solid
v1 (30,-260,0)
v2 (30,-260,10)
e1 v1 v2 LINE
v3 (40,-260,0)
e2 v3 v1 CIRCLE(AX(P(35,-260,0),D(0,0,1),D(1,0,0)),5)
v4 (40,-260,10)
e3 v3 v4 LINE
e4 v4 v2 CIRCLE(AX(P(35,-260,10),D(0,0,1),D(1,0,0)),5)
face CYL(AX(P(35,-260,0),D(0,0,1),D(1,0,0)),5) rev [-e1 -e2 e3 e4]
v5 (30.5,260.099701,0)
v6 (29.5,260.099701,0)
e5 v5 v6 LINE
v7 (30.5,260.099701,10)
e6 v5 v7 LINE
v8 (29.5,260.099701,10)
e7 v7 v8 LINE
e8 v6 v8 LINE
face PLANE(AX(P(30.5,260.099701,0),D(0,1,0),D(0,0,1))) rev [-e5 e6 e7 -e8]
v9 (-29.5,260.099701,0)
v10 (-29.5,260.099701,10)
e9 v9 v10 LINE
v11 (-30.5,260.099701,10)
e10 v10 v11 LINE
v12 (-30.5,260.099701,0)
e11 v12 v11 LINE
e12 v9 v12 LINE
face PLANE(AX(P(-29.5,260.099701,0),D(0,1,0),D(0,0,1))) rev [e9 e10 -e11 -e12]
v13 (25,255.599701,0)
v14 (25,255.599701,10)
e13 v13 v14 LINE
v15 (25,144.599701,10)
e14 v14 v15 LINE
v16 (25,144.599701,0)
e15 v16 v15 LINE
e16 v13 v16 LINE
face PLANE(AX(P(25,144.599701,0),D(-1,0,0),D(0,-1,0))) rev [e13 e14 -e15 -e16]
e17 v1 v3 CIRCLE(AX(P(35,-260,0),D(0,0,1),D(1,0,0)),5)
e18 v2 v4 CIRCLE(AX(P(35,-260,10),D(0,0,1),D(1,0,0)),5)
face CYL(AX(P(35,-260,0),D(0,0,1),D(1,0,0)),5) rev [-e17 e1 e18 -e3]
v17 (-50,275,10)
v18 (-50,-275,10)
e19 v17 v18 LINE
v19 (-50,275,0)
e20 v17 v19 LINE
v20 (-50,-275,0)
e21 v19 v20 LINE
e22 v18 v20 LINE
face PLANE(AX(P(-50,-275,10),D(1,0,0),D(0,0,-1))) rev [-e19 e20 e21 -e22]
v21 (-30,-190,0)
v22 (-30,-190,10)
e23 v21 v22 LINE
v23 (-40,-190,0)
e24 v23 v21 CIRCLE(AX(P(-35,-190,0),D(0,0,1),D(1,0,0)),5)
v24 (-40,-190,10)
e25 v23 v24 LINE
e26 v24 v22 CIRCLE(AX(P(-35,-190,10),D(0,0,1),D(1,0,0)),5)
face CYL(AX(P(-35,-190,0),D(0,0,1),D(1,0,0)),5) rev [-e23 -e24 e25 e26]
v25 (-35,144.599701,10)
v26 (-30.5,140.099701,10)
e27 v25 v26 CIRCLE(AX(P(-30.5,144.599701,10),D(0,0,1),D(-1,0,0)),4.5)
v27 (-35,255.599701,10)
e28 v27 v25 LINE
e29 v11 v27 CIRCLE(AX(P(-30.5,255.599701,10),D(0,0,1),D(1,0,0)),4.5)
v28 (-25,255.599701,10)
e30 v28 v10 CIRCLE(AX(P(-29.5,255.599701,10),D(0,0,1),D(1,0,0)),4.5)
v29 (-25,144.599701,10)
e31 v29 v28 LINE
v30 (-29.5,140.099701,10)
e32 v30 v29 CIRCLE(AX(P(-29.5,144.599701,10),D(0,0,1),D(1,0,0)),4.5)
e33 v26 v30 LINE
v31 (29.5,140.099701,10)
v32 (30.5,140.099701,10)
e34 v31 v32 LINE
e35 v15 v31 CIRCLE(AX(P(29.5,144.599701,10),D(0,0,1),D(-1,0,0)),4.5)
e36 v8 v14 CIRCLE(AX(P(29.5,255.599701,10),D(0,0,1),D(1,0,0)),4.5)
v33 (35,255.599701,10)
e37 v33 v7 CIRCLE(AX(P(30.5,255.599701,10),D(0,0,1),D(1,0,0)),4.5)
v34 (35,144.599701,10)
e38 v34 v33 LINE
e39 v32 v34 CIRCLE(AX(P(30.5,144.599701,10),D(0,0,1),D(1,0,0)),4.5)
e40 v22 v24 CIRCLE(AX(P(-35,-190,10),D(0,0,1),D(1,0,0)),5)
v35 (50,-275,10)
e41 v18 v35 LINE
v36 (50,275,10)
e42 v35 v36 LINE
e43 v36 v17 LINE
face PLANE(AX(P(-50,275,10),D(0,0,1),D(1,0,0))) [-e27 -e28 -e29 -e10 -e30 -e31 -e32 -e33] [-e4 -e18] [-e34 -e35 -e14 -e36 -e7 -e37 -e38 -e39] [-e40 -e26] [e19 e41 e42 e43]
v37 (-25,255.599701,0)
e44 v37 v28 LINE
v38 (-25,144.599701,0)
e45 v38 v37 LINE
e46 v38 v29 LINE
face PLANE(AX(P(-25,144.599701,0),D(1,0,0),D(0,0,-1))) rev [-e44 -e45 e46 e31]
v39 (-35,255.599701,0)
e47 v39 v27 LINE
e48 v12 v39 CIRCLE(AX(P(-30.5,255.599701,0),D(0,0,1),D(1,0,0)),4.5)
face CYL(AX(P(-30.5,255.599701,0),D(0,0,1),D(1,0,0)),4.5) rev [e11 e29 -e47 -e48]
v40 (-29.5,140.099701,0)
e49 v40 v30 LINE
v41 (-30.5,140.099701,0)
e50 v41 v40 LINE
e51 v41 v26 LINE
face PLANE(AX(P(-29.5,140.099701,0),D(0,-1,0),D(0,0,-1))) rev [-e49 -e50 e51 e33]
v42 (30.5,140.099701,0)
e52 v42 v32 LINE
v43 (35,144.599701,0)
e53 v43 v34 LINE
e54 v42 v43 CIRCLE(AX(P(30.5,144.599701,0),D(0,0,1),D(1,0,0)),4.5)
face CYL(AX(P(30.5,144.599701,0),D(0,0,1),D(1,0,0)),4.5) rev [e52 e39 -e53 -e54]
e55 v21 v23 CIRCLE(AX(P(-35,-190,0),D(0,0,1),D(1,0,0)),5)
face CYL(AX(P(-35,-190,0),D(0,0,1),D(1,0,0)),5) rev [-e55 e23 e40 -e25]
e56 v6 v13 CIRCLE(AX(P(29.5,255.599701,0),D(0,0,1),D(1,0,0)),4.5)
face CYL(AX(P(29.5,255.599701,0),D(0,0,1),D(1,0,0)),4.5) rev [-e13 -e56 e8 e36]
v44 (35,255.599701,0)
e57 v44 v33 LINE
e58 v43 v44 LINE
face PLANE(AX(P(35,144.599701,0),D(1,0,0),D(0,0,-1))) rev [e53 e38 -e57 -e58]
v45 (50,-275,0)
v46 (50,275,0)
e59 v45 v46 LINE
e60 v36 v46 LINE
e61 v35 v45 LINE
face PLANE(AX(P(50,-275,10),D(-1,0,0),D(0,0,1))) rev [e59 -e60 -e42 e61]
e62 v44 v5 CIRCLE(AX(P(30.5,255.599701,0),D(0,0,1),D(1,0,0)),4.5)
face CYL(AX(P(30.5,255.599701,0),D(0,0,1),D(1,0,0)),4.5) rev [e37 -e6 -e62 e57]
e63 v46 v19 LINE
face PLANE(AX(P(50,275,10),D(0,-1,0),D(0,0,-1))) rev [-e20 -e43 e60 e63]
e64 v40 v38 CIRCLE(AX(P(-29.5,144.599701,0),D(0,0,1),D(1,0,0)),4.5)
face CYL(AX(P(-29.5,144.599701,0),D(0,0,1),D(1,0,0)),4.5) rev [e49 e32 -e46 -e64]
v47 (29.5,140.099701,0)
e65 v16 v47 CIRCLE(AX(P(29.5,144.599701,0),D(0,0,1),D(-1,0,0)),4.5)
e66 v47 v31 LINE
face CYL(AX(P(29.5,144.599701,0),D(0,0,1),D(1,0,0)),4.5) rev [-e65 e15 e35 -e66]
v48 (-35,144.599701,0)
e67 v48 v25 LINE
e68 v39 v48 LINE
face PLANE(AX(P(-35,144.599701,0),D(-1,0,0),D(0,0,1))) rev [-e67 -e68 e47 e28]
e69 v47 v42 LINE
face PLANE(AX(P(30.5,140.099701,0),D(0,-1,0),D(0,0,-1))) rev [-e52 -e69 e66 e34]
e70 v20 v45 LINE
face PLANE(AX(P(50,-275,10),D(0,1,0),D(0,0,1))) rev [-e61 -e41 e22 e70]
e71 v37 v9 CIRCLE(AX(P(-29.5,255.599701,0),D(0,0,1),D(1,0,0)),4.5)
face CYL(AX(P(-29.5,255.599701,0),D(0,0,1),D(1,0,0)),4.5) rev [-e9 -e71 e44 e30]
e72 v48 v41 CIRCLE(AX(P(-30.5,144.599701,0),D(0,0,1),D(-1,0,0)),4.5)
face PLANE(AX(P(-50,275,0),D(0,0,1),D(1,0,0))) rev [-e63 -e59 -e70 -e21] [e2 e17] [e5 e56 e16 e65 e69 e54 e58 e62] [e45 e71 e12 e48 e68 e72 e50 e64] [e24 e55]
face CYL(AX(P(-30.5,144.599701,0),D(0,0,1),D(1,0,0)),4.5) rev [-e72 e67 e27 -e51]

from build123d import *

# Parameters (mm, degrees)
SKETCH1_W           = 100
SKETCH1_H           = 550
BOSS_EXTRUDE1_DEPTH = 10
SKETCH2_R           = 5
CUT_EXTRUDE1_DEPTH  = 10
CUT_EXTRUDE2_DEPTH  = 10


with BuildPart() as part:
    # Sketch1 → Boss-Extrude1 (new body)
    with BuildSketch(Plane.XY):
        Rectangle(SKETCH1_W, SKETCH1_H)
    extrude(amount=BOSS_EXTRUDE1_DEPTH)

    # Sketch2 → Cut-Extrude1 (cut)
    with BuildSketch(Plane.XY.offset(10)):
        with Locations((-35, -190)):
            Circle(SKETCH2_R)
        with Locations((35, -260)):
            Circle(SKETCH2_R)
    extrude(amount=-CUT_EXTRUDE1_DEPTH, mode=Mode.SUBTRACT)

    # Sketch3 → Cut-Extrude2 (cut)
    with BuildSketch(Plane.XY.offset(10)):
        with BuildLine():
            Line((-29.5, 140.099701054), (-30.5, 140.099701054))
            ThreePointArc((-30.5, 140.099701054), (-33.681980515, 141.417720539), (-35, 144.599701054))
            Line((-35, 144.599701054), (-35, 255.599701054))
            ThreePointArc((-35, 255.599701054), (-33.681980515, 258.78168157), (-30.5, 260.099701054))
            Line((-30.5, 260.099701054), (-29.5, 260.099701054))
            ThreePointArc((-29.5, 260.099701054), (-26.318019485, 258.78168157), (-25, 255.599701054))
            Line((-25, 255.599701054), (-25, 144.599701054))
            ThreePointArc((-25, 144.599701054), (-26.318019485, 141.417720539), (-29.5, 140.099701054))
        make_face()
        with BuildLine():
            Line((30.5, 140.099701054), (29.5, 140.099701054))
            ThreePointArc((29.5, 140.099701054), (26.318019485, 141.417720539), (25, 144.599701054))
            Line((25, 144.599701054), (25, 255.599701054))
            ThreePointArc((25, 255.599701054), (26.318019485, 258.78168157), (29.5, 260.099701054))
            Line((29.5, 260.099701054), (30.5, 260.099701054))
            ThreePointArc((30.5, 260.099701054), (33.681980515, 258.78168157), (35, 255.599701054))
            Line((35, 255.599701054), (35, 144.599701054))
            ThreePointArc((35, 144.599701054), (33.681980515, 141.417720539), (30.5, 140.099701054))
        make_face()
    extrude(amount=-CUT_EXTRUDE2_DEPTH, mode=Mode.SUBTRACT)


solid = part.part
